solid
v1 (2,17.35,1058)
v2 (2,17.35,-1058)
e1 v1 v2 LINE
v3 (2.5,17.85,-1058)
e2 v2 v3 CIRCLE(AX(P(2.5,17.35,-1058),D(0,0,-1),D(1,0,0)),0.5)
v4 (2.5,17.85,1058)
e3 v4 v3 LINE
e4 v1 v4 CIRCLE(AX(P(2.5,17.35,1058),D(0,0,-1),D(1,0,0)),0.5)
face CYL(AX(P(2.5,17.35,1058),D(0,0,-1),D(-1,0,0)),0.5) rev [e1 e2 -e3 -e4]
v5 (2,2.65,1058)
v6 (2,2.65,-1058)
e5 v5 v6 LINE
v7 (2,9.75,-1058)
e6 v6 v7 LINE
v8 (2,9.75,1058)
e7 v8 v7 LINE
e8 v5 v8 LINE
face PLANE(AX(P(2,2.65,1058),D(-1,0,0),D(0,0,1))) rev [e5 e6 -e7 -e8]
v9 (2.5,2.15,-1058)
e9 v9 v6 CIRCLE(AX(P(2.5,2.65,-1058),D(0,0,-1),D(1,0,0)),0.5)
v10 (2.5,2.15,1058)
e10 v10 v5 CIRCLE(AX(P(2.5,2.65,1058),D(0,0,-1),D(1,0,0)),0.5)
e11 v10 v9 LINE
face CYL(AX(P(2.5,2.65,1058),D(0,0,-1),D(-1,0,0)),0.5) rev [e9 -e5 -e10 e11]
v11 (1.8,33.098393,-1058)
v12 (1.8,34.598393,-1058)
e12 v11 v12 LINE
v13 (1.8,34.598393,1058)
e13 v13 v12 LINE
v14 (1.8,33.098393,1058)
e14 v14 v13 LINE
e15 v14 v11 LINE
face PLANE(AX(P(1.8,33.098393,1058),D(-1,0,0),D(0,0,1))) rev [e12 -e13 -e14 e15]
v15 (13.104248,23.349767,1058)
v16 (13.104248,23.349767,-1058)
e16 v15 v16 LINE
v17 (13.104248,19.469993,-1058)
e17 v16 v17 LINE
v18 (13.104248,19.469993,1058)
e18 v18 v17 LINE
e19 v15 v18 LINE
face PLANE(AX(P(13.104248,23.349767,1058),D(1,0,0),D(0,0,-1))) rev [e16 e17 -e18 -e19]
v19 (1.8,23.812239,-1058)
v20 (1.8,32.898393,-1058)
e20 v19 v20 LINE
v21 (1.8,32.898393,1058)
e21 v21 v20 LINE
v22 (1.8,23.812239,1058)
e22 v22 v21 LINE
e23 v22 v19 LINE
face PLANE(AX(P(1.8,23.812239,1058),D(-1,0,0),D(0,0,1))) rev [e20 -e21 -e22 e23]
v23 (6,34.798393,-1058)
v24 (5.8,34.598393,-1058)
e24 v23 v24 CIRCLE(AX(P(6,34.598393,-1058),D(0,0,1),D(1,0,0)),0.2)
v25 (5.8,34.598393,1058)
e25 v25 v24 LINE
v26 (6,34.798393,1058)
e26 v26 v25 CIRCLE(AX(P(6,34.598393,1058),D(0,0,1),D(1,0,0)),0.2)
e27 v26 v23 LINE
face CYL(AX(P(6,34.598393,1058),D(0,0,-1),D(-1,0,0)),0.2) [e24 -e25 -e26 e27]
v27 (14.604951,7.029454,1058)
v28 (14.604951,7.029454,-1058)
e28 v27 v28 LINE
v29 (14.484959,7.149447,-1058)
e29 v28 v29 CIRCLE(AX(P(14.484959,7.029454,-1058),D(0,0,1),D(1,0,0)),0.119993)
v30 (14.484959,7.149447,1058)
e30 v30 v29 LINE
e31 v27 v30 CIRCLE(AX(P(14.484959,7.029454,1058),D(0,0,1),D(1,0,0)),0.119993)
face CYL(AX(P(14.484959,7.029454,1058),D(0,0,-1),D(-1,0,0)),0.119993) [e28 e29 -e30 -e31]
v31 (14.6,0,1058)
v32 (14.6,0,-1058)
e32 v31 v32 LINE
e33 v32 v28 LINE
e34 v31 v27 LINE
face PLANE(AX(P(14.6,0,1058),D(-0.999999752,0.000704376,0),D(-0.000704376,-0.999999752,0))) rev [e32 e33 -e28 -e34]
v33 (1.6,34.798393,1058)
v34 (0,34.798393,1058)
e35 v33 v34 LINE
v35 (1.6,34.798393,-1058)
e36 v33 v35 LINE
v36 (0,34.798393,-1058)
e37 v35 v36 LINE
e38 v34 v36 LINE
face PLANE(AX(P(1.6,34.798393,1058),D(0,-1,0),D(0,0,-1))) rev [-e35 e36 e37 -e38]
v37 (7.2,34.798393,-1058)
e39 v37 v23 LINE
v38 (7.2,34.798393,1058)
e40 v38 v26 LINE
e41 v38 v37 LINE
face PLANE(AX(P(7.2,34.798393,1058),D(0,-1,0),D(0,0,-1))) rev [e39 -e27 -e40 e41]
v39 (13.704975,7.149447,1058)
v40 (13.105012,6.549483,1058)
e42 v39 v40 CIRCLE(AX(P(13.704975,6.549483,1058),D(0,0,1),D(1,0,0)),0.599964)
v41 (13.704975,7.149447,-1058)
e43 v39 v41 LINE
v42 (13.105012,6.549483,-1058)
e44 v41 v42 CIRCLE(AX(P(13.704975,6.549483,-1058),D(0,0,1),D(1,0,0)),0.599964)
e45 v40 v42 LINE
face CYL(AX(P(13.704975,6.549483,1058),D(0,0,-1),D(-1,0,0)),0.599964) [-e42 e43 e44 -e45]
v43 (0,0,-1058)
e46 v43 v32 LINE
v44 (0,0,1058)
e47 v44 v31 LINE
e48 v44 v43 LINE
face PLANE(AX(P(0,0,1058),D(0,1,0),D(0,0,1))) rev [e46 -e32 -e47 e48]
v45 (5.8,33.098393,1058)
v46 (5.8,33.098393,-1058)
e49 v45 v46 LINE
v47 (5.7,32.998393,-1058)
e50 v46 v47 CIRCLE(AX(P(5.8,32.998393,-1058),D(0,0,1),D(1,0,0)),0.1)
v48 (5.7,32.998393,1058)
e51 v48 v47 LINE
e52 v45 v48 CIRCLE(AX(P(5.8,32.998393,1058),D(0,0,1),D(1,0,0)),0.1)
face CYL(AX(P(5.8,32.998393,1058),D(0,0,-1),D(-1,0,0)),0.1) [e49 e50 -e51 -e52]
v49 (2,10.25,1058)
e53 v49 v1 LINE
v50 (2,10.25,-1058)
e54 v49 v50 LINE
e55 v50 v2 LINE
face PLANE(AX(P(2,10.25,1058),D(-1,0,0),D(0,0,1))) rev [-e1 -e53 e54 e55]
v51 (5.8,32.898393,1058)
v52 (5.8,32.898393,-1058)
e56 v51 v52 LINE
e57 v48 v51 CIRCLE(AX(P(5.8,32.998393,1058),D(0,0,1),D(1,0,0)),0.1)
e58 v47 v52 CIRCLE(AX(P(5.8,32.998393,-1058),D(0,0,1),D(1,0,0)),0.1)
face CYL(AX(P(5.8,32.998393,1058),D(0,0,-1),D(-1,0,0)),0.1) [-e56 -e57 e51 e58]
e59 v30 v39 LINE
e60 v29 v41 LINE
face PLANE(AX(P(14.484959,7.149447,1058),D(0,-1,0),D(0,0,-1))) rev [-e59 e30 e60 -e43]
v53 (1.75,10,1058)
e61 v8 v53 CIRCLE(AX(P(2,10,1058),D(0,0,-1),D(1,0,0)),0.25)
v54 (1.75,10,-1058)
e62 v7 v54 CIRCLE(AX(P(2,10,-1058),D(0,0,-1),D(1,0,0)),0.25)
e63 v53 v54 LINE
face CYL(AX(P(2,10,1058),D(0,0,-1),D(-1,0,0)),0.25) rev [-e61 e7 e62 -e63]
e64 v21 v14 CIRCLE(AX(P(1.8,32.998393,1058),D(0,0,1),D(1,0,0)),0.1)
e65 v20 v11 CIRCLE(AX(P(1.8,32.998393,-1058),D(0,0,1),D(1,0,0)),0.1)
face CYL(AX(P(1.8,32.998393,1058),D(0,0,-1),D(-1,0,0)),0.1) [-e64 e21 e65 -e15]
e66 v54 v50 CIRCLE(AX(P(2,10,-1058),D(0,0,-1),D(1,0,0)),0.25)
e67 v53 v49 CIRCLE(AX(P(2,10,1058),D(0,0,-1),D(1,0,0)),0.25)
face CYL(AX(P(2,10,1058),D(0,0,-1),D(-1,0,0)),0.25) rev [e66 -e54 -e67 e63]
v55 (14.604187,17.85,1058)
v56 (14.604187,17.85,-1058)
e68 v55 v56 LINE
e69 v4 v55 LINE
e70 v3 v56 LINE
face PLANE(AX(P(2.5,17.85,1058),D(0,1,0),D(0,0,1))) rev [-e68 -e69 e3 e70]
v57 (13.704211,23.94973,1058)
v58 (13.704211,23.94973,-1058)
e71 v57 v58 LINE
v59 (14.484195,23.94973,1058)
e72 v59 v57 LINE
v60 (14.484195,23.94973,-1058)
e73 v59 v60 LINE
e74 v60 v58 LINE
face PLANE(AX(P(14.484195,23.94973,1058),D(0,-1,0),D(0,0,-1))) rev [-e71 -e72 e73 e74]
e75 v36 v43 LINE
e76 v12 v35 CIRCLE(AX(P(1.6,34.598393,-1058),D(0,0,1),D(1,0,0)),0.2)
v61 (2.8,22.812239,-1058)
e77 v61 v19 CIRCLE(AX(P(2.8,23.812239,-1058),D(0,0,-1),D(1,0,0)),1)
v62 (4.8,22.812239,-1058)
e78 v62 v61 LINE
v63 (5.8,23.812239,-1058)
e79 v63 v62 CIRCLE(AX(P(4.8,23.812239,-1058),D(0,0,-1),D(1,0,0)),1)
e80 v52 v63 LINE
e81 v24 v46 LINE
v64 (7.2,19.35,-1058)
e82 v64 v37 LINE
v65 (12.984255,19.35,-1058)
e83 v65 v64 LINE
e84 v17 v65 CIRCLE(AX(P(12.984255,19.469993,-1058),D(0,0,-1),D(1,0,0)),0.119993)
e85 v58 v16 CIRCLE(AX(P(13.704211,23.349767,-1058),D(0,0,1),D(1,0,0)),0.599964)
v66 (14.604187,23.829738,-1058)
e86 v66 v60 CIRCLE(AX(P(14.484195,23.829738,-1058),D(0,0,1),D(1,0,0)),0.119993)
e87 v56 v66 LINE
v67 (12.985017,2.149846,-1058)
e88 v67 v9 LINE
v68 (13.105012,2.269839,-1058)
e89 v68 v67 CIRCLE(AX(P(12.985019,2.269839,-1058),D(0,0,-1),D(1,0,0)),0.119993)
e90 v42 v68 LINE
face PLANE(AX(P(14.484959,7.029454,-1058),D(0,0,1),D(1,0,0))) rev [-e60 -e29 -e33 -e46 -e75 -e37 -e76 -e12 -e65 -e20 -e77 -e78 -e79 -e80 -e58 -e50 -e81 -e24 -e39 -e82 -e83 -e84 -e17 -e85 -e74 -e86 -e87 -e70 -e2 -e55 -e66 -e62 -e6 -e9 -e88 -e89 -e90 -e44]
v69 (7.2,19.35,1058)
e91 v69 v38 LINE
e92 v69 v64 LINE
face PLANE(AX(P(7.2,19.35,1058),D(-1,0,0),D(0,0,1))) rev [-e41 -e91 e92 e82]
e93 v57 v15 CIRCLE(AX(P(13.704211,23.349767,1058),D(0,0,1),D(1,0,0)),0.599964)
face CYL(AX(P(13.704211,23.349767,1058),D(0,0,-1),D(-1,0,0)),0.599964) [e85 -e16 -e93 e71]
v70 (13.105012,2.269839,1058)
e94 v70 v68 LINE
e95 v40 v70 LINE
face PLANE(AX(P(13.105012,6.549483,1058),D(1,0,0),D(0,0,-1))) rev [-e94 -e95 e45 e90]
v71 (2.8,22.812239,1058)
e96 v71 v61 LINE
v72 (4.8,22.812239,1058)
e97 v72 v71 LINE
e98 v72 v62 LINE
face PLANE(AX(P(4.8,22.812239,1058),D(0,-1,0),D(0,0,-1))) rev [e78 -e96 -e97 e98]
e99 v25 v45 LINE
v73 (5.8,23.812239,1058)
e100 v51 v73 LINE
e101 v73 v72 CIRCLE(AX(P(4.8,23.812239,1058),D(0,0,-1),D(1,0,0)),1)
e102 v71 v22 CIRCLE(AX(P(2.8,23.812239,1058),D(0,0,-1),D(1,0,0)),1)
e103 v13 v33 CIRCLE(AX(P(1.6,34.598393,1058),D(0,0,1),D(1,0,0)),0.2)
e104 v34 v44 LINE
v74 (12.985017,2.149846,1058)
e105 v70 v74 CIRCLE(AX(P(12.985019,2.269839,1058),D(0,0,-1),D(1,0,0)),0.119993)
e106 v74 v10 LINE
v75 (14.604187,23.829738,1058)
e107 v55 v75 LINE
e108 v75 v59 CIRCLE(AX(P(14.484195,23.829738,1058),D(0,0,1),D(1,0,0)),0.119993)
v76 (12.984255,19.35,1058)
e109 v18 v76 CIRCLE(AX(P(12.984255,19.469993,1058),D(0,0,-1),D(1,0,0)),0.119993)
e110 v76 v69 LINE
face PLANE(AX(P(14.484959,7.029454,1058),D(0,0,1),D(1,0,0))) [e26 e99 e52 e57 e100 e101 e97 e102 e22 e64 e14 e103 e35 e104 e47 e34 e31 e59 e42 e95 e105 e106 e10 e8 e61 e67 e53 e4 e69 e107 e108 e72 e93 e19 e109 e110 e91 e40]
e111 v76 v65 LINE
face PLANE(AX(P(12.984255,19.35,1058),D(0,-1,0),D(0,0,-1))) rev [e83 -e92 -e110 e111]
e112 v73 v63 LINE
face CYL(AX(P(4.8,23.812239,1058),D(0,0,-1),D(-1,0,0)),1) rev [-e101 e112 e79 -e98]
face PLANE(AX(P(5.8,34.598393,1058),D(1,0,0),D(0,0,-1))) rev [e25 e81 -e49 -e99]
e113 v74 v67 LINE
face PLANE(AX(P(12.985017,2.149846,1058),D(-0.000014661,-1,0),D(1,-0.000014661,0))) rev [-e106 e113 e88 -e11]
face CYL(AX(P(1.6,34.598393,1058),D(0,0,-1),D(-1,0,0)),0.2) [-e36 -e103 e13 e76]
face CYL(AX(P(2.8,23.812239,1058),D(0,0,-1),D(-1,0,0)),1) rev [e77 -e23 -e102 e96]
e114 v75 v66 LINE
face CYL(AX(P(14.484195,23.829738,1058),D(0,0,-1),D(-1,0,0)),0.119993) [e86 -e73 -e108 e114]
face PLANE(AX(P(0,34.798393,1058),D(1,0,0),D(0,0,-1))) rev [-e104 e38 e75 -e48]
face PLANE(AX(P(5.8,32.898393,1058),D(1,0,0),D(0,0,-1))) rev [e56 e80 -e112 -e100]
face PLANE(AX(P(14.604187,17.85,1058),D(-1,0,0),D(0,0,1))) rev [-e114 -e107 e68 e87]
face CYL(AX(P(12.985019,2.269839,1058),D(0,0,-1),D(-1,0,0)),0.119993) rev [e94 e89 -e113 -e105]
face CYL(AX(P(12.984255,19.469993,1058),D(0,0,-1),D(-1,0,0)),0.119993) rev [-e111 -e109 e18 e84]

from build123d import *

# Parameters (mm, degrees)
EXTRUDE_1_DEPTH = 1058


with BuildPart() as part:
    # 草图2 → 凸台-拉伸1 (new, symmetric)
    with BuildSketch(Plane.XY):
        with BuildLine():
            Line((14.484958611, 7.149447031), (13.704975481, 7.149447031))
            ThreePointArc((13.704975481, 7.149447031), (13.280736974, 6.973721688), (13.105011631, 6.549483181))
            Line((13.105011631, 6.549483181), (13.105011631, 2.269839045))
            ThreePointArc((13.105011631, 2.269839045), (13.06986594, 2.184990722), (12.985017102, 2.149846275))
            Line((12.985017102, 2.149846275), (2.5, 2.15))
            ThreePointArc((2.5, 2.15), (2.146446609, 2.296446609), (2, 2.65))
            Line((2, 2.65), (2, 9.75))
            ThreePointArc((2, 9.75), (1.75, 10), (2, 10.25))
            Line((2, 10.25), (2, 17.35))
            ThreePointArc((2, 17.35), (2.146446609, 17.703553391), (2.5, 17.85))
            Line((2.5, 17.85), (14.604187277, 17.85))
            Line((14.604187277, 17.85), (14.604187277, 23.829737701))
            ThreePointArc((14.604187277, 23.829737701), (14.569042208, 23.914585402), (14.484194507, 23.949730471))
            Line((14.484194507, 23.949730471), (13.704211377, 23.949730471))
            ThreePointArc((13.704211377, 23.949730471), (13.27997287, 23.774005128), (13.104247527, 23.349766621))
            Line((13.104247527, 23.349766621), (13.104247527, 19.46999277))
            ThreePointArc((13.104247527, 19.46999277), (13.069102458, 19.385145069), (12.984254757, 19.35))
            Line((12.984254757, 19.35), (7.2, 19.35))
            Line((7.2, 19.35), (7.2, 34.798393128))
            Line((7.2, 34.798393128), (6, 34.798393128))
            ThreePointArc((6, 34.798393128), (5.858578644, 34.739814485), (5.8, 34.598393128))
            Line((5.8, 34.598393128), (5.8, 33.098393128))
            ThreePointArc((5.8, 33.098393128), (5.7, 32.998393128), (5.8, 32.898393128))
            Line((5.8, 32.898393128), (5.8, 23.812239282))
            ThreePointArc((5.8, 23.812239282), (5.507106781, 23.105132501), (4.8, 22.812239282))
            Line((4.8, 22.812239282), (2.8, 22.812239282))
            ThreePointArc((2.8, 22.812239282), (2.092893219, 23.105132501), (1.8, 23.812239282))
            Line((1.8, 23.812239282), (1.8, 32.898393128))
            ThreePointArc((1.8, 32.898393128), (1.9, 32.998393128), (1.8, 33.098393128))
            Line((1.8, 33.098393128), (1.8, 34.598393128))
            ThreePointArc((1.8, 34.598393128), (1.741421356, 34.739814485), (1.6, 34.798393128))
            Line((1.6, 34.798393128), (0, 34.798393128))
            Line((0, 34.798393128), (0, 0))
            Line((0, 0), (14.6, 0))
            Line((14.6, 0), (14.604951381, 7.029454261))
            ThreePointArc((14.604951381, 7.029454261), (14.569806312, 7.114301962), (14.484958611, 7.149447031))
        make_face()
    extrude(amount=EXTRUDE_1_DEPTH, both=True)


solid = part.part
